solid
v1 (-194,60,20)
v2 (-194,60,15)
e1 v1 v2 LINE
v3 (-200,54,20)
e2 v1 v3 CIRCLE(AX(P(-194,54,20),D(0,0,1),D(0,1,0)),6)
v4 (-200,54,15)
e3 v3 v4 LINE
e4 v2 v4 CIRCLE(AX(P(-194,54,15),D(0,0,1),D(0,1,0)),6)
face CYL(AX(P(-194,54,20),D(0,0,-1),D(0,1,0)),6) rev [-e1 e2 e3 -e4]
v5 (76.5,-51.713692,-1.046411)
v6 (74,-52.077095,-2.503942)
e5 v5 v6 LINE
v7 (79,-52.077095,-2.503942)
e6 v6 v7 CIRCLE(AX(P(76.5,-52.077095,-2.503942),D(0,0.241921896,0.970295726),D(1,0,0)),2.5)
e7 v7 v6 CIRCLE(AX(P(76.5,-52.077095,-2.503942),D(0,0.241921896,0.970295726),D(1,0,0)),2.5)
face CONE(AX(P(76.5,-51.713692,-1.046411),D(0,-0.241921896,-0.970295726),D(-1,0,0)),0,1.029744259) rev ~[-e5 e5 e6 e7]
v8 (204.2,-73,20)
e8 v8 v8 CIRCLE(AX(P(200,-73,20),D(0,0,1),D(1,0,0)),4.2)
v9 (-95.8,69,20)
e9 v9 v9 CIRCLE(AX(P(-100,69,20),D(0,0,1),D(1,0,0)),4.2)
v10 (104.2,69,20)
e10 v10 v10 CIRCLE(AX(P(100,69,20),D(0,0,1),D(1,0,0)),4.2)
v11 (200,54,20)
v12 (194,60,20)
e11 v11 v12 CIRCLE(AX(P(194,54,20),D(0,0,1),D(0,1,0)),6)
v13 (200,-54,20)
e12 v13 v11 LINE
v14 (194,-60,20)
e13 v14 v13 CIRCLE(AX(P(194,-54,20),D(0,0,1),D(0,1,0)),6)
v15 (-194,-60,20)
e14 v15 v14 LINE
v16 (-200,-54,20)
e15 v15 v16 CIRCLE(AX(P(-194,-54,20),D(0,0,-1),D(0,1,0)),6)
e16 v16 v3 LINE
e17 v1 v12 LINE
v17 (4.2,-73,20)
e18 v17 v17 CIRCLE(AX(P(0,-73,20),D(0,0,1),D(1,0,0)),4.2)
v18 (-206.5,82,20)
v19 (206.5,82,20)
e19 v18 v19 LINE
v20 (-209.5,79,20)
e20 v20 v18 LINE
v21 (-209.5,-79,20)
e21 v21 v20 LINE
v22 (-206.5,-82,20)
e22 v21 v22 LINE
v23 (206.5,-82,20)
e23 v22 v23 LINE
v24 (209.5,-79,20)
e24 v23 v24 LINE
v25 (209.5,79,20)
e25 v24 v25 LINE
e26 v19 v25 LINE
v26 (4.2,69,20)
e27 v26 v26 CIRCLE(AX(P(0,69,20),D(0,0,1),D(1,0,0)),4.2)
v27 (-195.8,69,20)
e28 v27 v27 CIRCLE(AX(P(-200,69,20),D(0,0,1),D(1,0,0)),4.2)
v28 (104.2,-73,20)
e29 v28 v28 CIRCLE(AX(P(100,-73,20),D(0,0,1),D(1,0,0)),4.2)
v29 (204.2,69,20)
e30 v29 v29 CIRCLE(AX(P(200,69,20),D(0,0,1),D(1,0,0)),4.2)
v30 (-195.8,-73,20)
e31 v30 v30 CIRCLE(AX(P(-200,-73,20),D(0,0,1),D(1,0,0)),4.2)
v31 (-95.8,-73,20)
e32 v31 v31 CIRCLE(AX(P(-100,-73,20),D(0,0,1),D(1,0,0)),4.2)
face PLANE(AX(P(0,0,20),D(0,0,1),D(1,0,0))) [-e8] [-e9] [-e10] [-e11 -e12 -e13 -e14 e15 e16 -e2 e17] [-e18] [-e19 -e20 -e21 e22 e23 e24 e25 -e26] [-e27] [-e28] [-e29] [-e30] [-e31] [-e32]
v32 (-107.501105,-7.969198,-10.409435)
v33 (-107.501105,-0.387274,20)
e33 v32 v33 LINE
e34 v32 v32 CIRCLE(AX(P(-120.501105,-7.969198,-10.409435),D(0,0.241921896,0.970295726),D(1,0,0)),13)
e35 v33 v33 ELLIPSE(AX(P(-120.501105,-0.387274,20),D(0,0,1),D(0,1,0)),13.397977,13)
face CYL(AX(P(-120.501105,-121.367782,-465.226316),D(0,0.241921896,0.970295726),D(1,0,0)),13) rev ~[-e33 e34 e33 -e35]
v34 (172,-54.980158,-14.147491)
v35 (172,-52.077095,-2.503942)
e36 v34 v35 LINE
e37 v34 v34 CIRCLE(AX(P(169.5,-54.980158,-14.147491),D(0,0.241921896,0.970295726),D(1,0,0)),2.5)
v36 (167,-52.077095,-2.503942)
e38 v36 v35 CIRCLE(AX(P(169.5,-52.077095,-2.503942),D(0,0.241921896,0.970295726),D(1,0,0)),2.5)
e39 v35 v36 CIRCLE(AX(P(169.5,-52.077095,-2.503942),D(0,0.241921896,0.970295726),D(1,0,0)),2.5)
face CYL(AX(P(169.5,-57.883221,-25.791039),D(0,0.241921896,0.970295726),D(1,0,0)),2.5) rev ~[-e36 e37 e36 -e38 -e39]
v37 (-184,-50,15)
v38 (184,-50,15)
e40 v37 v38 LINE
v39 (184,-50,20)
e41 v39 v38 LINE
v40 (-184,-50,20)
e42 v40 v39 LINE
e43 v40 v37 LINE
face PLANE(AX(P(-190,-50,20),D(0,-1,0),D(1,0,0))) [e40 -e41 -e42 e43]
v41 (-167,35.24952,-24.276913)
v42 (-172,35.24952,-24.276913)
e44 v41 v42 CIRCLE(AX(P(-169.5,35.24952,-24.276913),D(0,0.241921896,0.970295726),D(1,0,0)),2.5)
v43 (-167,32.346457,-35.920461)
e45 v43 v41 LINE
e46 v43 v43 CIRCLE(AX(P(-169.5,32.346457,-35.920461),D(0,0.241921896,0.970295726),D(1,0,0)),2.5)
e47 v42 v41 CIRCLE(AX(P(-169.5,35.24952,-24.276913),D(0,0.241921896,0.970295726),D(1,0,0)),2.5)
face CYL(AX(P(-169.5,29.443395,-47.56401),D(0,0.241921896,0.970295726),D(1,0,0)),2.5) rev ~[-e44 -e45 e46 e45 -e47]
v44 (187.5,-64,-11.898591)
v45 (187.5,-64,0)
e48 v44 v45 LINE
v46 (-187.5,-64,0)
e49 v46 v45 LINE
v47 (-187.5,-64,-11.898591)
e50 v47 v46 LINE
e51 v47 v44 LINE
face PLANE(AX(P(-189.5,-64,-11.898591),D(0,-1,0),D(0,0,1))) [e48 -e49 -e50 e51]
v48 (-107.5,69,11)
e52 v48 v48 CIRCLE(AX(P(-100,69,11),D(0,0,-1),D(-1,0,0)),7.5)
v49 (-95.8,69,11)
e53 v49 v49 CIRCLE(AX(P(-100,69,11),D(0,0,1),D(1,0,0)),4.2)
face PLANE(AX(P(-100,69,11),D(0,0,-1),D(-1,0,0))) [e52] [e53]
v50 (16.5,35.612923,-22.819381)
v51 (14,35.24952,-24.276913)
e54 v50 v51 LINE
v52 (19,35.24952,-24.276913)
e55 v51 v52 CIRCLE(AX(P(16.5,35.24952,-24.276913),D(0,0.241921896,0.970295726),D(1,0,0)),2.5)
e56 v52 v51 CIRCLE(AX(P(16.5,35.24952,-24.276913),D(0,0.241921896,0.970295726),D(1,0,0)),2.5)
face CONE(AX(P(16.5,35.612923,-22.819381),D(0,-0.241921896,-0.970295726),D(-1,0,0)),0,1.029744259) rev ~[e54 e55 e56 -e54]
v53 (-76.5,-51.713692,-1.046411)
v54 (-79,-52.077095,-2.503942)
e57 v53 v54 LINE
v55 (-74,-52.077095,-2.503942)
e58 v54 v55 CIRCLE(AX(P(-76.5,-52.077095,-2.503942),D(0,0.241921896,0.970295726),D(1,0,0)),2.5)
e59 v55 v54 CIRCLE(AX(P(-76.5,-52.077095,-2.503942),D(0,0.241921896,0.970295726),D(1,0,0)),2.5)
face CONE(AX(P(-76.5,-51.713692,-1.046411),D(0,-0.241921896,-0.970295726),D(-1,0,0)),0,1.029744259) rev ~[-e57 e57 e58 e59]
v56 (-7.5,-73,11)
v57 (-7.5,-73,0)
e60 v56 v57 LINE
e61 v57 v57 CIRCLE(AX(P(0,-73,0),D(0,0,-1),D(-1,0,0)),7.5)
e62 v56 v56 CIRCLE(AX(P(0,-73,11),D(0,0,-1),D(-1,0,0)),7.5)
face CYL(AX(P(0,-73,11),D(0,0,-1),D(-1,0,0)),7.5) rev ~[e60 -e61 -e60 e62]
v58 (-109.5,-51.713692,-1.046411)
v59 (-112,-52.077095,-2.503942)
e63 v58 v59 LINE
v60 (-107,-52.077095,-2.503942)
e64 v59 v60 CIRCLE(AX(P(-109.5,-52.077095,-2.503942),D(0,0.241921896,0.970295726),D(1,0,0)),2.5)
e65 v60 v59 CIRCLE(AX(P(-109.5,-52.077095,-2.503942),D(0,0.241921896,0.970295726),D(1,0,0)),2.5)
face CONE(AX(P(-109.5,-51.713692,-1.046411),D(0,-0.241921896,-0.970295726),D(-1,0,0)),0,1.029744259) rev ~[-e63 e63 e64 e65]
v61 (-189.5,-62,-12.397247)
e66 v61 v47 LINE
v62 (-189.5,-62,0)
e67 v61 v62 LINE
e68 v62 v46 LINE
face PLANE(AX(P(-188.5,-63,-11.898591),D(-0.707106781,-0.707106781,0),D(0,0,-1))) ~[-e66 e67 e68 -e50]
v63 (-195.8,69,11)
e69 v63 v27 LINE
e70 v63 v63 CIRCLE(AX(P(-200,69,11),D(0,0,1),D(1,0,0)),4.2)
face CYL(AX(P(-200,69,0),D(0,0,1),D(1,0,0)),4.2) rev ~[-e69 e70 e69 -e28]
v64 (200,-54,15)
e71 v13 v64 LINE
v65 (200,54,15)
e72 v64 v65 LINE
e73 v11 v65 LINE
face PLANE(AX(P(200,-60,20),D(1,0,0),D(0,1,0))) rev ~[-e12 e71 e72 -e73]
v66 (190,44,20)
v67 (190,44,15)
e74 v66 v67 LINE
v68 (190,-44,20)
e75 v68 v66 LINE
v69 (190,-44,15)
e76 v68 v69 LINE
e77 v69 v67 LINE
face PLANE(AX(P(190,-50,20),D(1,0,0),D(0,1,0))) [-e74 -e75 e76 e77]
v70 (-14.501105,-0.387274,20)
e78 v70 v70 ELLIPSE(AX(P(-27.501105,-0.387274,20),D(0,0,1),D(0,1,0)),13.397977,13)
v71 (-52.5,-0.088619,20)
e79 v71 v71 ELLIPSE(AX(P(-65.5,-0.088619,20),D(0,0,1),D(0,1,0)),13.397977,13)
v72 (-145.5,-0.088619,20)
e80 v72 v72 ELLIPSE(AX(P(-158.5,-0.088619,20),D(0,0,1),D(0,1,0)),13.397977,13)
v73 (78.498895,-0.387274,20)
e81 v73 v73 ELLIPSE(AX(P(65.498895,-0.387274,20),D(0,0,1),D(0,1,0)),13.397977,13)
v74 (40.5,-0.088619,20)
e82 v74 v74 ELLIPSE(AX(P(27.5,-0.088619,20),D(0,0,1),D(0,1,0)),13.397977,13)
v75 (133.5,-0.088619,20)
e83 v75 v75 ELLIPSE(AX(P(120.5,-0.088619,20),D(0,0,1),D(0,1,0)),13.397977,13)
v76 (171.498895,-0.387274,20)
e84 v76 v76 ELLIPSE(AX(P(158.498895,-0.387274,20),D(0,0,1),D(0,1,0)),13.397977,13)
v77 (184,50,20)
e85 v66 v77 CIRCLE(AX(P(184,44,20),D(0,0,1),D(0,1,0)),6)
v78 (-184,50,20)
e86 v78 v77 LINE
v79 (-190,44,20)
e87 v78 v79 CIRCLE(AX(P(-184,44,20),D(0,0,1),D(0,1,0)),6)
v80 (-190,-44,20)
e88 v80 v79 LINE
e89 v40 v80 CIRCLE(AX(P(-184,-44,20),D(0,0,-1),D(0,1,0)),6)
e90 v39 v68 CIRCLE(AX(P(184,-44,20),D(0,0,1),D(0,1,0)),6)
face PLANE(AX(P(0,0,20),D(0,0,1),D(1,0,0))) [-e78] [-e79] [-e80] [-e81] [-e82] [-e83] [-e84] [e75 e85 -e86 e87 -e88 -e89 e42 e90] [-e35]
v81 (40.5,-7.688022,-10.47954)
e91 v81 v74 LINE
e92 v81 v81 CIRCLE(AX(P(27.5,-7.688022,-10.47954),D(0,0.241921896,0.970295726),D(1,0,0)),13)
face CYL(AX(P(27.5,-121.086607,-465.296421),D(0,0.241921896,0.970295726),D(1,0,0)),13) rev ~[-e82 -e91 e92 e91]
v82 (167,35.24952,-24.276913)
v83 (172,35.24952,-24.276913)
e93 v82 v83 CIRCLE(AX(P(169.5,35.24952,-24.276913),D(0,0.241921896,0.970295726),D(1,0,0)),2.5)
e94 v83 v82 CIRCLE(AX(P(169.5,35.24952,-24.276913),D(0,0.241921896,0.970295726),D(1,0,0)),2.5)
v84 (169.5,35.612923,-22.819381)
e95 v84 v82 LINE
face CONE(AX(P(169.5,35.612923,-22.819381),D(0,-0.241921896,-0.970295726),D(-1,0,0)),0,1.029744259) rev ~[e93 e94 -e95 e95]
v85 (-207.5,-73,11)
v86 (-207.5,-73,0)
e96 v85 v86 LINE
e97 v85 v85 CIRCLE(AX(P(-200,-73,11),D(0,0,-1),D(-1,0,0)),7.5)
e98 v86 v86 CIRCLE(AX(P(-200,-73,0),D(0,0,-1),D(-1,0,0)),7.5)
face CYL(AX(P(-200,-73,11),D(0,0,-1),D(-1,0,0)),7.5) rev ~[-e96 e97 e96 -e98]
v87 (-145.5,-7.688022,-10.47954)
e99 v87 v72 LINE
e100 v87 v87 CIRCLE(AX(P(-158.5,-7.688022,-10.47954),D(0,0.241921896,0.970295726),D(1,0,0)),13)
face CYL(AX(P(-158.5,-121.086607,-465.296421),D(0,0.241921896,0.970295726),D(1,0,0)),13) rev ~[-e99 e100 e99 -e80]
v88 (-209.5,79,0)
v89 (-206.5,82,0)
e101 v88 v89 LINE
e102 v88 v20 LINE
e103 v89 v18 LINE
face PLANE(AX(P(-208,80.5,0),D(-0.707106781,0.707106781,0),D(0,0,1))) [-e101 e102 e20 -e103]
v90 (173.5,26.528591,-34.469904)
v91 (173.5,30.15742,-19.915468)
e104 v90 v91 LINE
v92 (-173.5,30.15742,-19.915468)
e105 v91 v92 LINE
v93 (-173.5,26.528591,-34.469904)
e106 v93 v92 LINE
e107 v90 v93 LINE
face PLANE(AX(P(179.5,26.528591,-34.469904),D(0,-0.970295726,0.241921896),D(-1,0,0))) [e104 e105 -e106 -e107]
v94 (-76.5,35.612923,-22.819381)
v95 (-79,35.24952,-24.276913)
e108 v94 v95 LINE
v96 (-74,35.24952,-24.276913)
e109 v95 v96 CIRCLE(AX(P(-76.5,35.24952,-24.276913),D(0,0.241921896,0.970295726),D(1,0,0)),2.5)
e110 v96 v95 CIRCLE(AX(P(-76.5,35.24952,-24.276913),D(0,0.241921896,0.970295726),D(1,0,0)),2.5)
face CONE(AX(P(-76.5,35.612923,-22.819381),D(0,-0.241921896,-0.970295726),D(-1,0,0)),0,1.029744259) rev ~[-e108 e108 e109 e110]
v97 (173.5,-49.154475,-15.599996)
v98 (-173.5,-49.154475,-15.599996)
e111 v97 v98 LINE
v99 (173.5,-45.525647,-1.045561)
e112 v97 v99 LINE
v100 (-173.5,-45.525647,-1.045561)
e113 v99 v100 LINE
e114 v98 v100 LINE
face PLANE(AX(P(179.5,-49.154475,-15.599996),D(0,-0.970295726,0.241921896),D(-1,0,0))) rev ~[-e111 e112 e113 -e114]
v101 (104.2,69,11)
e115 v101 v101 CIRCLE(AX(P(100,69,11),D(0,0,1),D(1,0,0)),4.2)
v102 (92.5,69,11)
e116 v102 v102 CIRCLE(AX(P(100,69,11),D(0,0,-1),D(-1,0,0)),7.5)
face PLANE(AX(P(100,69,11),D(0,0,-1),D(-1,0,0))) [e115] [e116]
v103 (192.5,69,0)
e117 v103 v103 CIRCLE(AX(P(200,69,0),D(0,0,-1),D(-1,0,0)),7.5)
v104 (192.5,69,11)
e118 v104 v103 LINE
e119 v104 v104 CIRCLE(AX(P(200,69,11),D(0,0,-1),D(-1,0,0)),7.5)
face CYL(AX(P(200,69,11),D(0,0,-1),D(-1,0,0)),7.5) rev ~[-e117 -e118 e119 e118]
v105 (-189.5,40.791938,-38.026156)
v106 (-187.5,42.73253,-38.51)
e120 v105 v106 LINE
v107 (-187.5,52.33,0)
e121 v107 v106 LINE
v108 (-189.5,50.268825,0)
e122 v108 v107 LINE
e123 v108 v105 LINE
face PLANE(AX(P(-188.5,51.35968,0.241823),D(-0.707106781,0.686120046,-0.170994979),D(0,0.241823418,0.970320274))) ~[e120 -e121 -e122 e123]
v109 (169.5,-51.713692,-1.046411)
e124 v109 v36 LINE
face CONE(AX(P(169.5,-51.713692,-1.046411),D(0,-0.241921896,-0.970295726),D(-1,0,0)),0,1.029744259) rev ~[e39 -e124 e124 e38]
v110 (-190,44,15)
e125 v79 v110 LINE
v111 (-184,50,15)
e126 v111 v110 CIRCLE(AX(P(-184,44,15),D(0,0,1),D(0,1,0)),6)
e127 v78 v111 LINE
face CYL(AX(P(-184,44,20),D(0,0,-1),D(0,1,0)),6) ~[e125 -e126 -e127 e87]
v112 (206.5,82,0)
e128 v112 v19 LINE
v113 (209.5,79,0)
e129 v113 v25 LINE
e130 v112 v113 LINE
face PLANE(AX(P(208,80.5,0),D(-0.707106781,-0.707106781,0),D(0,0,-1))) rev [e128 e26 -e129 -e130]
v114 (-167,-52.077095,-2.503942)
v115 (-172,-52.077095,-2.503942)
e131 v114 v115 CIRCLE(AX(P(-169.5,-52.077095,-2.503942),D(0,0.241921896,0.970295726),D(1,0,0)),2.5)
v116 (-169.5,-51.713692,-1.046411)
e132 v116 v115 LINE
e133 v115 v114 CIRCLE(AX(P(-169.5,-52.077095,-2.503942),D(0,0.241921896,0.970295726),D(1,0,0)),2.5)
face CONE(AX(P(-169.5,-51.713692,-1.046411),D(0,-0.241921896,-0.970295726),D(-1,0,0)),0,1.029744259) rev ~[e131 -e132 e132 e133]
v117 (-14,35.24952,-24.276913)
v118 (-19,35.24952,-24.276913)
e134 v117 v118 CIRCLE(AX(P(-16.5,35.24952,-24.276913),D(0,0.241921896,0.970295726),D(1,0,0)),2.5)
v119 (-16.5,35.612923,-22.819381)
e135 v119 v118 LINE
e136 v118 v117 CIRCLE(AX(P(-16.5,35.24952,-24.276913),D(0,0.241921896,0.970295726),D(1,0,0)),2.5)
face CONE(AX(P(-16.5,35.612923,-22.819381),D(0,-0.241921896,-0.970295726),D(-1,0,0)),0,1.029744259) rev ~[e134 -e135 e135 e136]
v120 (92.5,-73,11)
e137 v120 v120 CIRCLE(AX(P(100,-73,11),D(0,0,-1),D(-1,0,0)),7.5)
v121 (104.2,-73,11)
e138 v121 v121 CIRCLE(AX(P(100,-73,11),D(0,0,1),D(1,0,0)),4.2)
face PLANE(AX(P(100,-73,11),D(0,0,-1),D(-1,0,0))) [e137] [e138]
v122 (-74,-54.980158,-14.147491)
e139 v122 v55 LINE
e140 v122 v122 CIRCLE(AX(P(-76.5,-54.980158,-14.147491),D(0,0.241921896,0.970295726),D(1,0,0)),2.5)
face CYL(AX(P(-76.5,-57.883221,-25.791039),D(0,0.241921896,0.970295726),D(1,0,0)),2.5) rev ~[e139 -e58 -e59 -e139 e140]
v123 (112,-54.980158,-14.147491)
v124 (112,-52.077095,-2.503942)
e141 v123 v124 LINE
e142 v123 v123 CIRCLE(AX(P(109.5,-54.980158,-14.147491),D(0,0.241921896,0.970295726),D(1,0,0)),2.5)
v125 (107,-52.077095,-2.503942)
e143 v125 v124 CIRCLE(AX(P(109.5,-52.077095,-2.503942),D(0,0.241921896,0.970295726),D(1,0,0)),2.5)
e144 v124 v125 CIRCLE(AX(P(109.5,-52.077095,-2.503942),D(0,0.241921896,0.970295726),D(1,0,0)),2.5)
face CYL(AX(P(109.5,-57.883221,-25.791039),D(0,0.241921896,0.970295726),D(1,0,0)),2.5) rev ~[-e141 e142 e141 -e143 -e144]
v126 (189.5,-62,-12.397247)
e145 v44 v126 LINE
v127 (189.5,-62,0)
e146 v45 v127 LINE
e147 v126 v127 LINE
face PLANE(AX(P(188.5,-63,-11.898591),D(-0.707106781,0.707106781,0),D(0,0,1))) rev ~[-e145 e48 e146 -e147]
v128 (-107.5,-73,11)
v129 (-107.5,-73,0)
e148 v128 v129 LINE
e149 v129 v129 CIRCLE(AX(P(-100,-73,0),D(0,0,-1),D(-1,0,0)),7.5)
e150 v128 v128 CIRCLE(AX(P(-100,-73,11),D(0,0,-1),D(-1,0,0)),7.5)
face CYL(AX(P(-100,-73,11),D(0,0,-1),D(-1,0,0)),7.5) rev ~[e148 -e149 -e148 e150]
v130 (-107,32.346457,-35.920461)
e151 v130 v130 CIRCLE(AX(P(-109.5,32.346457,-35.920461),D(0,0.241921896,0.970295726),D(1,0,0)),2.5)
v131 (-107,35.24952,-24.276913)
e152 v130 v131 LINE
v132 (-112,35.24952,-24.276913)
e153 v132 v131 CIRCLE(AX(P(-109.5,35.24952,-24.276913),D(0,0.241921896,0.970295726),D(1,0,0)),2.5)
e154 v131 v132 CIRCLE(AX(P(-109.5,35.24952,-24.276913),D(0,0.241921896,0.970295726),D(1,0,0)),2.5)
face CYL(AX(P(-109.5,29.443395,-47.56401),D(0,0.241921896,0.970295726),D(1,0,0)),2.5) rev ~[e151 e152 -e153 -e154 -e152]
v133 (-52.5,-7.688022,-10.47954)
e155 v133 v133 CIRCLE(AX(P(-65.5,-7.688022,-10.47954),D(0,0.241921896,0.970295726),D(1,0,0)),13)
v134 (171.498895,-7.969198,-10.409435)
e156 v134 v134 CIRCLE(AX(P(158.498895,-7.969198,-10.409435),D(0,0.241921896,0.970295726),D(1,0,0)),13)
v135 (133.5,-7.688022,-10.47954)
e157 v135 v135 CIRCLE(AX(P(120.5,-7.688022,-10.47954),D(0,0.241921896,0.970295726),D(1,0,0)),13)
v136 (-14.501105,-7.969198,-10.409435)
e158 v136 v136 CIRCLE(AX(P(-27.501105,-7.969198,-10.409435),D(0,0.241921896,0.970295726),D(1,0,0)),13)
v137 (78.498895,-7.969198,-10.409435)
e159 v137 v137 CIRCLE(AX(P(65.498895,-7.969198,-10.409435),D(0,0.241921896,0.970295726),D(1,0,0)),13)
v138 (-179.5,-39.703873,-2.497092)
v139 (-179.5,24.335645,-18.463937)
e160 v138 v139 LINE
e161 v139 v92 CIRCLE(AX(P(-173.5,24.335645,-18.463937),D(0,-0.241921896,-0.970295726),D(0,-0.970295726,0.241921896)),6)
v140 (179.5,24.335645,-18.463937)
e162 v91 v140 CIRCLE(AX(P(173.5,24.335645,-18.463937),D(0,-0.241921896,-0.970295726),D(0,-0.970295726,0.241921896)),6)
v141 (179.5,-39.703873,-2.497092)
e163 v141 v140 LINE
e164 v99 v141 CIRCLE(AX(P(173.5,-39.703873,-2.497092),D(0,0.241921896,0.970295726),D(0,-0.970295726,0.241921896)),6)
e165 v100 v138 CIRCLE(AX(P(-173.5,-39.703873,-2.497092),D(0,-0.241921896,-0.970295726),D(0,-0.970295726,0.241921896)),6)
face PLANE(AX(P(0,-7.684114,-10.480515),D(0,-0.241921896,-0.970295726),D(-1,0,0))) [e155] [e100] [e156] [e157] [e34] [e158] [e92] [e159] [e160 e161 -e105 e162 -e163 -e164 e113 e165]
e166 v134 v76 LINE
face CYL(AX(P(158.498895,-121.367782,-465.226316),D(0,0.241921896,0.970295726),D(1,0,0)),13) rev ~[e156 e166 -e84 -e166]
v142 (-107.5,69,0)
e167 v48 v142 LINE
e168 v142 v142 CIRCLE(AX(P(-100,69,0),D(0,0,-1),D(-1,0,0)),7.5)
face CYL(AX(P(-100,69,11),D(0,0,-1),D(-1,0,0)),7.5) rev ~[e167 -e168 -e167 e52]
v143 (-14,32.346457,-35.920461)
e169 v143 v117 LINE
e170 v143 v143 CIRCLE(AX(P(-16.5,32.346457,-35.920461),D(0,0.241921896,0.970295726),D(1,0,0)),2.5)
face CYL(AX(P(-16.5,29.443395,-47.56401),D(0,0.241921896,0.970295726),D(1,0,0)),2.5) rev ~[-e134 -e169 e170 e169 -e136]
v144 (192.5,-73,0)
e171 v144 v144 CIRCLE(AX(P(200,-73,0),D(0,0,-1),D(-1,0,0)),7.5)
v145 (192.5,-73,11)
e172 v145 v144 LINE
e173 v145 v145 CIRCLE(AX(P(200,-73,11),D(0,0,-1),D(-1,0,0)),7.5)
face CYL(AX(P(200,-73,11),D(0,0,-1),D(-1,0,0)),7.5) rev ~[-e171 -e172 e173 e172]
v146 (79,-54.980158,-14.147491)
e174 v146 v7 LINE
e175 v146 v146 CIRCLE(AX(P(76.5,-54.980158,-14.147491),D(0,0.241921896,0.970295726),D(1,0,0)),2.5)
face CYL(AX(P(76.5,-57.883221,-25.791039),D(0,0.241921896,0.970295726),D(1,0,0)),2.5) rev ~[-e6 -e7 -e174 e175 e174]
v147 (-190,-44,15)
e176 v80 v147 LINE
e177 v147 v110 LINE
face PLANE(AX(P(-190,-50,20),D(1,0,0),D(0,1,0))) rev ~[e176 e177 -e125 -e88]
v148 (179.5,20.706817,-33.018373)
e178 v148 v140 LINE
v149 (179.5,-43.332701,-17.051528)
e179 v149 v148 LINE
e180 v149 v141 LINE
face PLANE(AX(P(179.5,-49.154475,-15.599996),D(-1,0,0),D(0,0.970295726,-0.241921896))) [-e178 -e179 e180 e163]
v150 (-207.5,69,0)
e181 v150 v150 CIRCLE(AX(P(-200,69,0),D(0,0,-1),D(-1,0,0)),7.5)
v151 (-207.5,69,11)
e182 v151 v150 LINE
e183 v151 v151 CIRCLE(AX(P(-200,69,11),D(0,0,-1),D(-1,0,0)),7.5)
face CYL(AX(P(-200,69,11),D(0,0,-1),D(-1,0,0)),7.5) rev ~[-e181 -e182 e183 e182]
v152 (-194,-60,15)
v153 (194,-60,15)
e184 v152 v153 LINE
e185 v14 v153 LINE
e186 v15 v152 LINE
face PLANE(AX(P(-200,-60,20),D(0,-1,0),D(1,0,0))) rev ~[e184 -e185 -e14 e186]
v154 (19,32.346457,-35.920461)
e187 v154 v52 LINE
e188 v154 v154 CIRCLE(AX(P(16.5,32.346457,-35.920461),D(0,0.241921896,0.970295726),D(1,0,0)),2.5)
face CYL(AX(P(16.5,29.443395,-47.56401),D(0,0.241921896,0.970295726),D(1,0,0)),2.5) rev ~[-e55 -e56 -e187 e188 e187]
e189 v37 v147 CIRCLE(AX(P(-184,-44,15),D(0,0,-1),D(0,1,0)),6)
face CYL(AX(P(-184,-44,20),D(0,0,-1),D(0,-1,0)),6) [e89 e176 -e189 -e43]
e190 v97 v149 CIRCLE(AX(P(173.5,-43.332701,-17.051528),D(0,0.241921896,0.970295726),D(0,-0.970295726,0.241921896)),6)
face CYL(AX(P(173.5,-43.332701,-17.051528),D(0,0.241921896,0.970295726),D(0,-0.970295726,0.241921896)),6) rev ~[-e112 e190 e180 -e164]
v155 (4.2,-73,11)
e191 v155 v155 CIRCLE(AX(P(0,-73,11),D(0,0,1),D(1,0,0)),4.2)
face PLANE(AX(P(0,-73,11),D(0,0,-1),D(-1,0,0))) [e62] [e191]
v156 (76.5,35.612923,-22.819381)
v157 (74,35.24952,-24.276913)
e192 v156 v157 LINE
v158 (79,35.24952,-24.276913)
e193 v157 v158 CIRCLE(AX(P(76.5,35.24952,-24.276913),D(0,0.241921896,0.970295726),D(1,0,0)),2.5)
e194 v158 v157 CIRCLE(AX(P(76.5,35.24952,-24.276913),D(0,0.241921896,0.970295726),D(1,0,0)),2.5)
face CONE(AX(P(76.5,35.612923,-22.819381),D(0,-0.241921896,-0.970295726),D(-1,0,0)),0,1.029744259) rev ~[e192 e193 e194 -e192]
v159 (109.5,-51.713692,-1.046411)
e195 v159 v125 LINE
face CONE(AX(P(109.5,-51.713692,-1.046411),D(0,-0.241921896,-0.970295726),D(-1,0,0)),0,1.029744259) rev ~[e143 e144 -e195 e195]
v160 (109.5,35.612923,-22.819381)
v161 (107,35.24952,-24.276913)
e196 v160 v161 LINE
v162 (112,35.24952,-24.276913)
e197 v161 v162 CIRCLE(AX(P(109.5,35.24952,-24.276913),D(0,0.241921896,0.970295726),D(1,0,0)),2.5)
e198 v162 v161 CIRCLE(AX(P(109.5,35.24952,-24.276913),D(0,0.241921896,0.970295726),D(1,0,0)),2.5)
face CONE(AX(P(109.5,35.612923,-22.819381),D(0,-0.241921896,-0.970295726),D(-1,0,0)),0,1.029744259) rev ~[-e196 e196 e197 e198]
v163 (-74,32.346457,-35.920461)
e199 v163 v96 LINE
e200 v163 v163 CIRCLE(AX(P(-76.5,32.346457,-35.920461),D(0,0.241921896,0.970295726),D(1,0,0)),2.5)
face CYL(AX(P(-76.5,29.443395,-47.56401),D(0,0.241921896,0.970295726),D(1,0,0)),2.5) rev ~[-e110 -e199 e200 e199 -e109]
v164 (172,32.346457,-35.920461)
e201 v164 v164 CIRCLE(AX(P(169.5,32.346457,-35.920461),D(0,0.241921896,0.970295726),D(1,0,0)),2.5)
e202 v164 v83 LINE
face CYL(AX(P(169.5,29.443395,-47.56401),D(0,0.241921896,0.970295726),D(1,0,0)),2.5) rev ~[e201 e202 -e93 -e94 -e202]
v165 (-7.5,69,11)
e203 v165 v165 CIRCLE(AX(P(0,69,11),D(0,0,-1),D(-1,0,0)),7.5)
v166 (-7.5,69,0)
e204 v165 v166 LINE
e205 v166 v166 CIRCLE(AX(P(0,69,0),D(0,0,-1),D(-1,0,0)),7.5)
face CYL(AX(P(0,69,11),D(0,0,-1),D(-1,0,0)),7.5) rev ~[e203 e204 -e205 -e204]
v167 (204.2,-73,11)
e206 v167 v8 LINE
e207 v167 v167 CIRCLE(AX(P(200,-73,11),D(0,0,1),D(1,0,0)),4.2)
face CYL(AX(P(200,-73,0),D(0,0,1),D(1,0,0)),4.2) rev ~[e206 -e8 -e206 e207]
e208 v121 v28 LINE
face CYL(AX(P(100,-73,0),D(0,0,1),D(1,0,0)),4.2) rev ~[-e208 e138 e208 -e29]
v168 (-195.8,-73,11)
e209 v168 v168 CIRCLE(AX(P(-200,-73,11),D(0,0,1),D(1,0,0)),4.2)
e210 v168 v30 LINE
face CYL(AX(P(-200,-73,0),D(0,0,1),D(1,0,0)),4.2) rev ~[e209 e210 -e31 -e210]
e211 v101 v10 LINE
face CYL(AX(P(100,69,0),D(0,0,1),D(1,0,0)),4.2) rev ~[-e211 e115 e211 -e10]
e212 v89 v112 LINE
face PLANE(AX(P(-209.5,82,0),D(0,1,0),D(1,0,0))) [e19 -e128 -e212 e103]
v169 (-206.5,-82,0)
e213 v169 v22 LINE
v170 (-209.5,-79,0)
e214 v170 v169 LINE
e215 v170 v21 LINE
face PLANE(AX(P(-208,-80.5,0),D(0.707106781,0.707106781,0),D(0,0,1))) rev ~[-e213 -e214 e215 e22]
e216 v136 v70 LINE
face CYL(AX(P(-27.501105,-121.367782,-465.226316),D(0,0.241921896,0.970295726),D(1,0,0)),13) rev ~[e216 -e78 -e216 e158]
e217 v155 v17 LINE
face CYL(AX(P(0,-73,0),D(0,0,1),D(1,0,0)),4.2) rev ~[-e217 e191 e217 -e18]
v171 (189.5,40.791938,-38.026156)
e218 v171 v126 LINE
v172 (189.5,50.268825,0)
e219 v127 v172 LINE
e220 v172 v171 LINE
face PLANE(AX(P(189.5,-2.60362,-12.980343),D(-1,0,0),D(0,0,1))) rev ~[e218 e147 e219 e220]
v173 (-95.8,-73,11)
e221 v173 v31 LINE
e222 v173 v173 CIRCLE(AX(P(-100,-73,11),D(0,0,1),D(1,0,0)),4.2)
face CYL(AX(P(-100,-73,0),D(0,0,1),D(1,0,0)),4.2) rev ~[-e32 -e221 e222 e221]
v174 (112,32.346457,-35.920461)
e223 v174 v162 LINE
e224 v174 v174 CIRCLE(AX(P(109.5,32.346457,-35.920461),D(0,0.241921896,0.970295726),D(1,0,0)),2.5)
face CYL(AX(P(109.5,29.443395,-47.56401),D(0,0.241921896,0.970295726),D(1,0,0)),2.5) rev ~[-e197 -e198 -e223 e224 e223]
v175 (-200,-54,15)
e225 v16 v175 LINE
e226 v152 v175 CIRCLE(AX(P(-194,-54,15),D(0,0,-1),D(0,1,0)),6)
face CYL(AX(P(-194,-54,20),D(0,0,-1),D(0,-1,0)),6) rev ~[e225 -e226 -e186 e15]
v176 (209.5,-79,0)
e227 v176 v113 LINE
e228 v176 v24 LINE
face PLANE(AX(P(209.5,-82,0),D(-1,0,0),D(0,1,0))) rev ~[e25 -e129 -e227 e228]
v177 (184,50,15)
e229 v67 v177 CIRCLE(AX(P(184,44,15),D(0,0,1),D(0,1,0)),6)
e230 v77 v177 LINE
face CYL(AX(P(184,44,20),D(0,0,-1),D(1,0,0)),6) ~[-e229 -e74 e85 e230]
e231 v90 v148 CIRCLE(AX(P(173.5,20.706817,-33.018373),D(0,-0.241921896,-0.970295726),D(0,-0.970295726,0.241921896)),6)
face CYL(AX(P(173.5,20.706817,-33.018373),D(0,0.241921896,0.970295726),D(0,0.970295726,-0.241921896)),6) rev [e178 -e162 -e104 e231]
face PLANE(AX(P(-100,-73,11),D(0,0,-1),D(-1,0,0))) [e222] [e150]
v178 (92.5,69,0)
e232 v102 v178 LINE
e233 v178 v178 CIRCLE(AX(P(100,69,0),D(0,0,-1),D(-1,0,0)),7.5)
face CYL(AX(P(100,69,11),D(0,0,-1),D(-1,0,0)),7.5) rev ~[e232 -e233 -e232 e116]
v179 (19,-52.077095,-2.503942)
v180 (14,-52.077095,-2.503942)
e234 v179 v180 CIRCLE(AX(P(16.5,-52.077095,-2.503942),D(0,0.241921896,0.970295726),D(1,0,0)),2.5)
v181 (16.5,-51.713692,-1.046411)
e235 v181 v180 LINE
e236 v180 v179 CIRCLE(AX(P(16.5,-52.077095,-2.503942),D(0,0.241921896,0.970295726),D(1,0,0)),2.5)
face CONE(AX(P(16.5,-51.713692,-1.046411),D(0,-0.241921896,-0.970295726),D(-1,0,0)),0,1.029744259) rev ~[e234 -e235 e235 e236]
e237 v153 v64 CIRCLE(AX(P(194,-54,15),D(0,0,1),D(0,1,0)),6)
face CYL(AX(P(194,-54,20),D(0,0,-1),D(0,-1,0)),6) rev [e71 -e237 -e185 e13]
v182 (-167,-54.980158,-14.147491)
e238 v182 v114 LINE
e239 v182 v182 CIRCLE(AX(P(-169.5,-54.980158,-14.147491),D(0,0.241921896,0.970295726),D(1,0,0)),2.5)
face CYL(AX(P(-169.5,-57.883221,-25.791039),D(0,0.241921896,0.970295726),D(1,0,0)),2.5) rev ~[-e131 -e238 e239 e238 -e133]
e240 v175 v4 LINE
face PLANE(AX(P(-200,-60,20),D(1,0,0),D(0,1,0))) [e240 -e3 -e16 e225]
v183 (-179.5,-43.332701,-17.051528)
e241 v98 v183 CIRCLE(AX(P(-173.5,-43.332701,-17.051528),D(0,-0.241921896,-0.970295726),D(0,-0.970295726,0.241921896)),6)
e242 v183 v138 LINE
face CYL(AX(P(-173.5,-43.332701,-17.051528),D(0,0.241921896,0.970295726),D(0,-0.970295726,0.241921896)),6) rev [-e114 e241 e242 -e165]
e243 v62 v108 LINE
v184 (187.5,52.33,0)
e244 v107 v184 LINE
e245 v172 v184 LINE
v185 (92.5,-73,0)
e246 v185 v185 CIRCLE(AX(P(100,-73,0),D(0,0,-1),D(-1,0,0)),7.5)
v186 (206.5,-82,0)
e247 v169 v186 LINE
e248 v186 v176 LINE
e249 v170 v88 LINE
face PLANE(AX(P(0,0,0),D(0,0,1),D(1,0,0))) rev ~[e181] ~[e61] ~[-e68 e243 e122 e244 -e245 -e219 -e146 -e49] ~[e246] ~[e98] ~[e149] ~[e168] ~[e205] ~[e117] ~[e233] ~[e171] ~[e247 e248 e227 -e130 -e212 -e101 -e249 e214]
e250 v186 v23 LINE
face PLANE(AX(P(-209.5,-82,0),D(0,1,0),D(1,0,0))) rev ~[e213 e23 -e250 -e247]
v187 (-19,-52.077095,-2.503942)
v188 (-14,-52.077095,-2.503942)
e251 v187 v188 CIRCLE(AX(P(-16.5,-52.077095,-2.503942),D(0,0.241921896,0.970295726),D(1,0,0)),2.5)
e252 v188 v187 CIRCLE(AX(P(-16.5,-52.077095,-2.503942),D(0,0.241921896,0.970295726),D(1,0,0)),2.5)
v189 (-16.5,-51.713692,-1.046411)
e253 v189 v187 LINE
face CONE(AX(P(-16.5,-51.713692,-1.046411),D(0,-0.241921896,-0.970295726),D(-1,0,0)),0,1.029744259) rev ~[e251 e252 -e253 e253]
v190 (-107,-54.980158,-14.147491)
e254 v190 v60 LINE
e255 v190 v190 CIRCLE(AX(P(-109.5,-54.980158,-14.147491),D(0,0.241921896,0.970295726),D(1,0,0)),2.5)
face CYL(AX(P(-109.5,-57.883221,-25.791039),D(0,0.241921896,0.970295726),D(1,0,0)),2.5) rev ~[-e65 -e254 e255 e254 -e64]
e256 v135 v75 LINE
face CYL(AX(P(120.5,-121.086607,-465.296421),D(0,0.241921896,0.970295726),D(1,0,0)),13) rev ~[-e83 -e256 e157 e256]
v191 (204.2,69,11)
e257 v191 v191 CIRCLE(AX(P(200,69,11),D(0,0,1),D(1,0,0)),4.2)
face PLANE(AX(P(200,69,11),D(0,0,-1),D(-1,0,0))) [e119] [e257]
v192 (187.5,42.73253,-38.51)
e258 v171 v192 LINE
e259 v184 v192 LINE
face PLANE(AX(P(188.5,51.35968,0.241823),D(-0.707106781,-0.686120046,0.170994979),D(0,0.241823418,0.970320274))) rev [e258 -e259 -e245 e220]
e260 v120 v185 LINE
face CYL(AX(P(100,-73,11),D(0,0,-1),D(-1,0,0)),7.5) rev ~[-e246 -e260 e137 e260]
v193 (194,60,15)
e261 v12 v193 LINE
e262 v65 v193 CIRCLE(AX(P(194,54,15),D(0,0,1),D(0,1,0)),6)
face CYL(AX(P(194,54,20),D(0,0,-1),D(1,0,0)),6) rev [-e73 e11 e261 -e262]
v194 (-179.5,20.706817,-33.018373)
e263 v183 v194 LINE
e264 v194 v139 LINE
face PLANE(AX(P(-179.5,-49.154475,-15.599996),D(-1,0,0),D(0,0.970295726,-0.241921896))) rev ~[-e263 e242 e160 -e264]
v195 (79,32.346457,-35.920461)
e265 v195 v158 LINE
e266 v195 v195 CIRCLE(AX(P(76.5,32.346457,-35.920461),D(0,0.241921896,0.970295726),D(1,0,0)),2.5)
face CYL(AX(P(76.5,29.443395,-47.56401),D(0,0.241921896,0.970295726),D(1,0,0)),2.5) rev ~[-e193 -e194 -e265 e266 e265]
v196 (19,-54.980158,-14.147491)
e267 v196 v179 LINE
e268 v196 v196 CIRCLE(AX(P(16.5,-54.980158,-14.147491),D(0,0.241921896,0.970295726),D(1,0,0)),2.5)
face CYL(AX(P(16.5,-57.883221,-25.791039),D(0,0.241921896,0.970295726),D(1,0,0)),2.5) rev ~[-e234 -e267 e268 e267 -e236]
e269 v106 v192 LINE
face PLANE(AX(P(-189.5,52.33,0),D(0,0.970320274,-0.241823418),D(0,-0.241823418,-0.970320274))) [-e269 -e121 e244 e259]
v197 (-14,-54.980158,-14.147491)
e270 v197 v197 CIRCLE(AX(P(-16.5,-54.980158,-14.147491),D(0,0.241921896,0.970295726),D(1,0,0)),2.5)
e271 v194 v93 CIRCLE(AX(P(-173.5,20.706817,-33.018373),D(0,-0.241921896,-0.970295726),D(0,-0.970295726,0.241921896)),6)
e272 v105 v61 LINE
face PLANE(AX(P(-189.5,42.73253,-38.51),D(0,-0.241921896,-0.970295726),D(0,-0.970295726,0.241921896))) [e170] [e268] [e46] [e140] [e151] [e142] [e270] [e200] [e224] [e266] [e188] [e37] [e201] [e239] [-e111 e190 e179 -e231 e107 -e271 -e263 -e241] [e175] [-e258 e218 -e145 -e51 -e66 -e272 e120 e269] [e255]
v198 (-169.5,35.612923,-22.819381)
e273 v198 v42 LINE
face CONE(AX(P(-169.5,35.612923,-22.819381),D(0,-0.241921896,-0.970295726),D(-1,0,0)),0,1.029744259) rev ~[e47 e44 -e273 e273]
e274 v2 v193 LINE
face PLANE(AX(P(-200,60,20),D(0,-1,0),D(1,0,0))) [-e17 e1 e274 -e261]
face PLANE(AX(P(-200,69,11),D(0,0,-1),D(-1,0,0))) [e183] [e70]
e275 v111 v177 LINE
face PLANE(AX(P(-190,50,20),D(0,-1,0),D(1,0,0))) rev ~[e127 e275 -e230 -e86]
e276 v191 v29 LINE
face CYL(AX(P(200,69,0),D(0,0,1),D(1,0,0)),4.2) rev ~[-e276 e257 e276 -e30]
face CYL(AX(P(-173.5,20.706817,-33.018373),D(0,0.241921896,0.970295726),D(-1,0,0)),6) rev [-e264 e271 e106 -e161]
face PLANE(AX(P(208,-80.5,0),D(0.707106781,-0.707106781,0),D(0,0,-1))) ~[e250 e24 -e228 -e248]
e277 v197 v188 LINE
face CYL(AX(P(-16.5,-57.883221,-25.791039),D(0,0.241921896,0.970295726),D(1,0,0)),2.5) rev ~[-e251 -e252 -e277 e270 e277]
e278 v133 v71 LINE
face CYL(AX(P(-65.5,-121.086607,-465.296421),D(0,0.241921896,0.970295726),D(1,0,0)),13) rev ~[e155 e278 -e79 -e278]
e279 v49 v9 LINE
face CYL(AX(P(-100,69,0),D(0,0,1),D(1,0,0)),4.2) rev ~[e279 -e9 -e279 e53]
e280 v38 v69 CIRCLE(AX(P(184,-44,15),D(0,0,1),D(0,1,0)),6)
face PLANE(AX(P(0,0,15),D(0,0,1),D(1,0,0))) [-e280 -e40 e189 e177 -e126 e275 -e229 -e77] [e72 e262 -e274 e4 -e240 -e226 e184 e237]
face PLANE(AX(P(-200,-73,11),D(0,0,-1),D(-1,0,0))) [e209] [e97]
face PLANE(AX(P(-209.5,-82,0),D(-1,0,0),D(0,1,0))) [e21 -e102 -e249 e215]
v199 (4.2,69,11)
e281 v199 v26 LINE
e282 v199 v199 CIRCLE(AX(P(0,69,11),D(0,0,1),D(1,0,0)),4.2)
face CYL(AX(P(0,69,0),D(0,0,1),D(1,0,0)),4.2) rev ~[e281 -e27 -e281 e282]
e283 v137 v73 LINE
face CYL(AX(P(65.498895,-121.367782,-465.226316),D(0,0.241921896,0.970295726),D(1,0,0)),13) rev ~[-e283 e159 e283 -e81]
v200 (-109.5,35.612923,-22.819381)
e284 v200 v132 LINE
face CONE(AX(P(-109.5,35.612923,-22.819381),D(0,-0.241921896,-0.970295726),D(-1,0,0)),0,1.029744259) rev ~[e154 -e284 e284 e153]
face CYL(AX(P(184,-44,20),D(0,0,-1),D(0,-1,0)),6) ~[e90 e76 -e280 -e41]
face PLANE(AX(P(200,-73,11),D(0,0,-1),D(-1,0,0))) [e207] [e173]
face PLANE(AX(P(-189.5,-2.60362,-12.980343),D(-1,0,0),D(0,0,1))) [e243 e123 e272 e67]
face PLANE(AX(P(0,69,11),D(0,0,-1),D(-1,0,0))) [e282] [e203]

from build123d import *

# Parameters (mm, degrees)
SKETCH1_W             = 419
SKETCH1_H             = 164
BOSS_EXTRUDE1_DEPTH   = 20
SKETCH2_W             = 400
SKETCH2_H             = 120
SKETCH2_W_2           = 380
SKETCH2_H_2           = 100
CUT_EXTRUDE1_DEPTH    = 5
FILLET1_R             = 6
CHAMFER1_SIZE         = 3
HOLE1_D               = 8.4
HOLE1_CBORE_D         = 15
HOLE1_CBORE_DEPTH     = 11
BOSS_EXTRUDE2_DEPTH   = 379
CHAMFER2_SIZE         = 2
HOLE2_D               = 26
M6_TAPPED_HOLE1_D     = 5
M6_TAPPED_HOLE1_DEPTH = 12
M6_TAPPED_HOLE1_TIP   = 1.502151548
SKETCH12_W            = 359
SKETCH12_H            = 78
CUT_EXTRUDE2_DEPTH    = 15
FILLET2_R             = 6


with BuildPart() as part:
    # Sketch1 → Boss-Extrude1 (new body)
    with BuildSketch(Plane.XY):
        Rectangle(SKETCH1_W, SKETCH1_H)
    extrude(amount=BOSS_EXTRUDE1_DEPTH)

    # Sketch2 → Cut-Extrude1 (cut)
    with BuildSketch(Plane.XY.offset(20)):
        Rectangle(SKETCH2_W, SKETCH2_H)
        Rectangle(SKETCH2_W_2, SKETCH2_H_2, mode=Mode.SUBTRACT)
    extrude(amount=-CUT_EXTRUDE1_DEPTH, mode=Mode.SUBTRACT)

    # Fillet1
    fillet1_edges = [part.edges().sort_by_distance(p)[0] for p in [
        (200, 60, 17.5),
        (200, -60, 17.5),
        (-200, -60, 17.5),
        (-200, 60, 17.5),
        (190, -50, 17.5),
        (-190, -50, 17.5),
        (-190, 50, 17.5),
        (190, 50, 17.5),
    ]]
    fillet(fillet1_edges, radius=FILLET1_R)

    # Chamfer1
    chamfer1_edges = [part.edges().sort_by_distance(p)[0] for p in [
        (209.5, -82, 10),
        (-209.5, -82, 10),
        (-209.5, 82, 10),
        (209.5, 82, 10),
    ]]
    chamfer(chamfer1_edges, length=CHAMFER1_SIZE)

    # Hole1 (through all)
    with Locations(Plane(origin=(0, 0, 0), x_dir=(-1, 0, 0), z_dir=(0, 0, -1))):
        with Locations((-200, 69), (-200, -73), (-100, -73), (0, -73), (100, -73), (200, -73), (200, 69), (100, 69), (0, 69), (-100, 69)):
            CounterBoreHole(HOLE1_D / 2, HOLE1_CBORE_D / 2, HOLE1_CBORE_DEPTH)

    # Sketch6 → Boss-Extrude2 (add)
    with BuildSketch(Plane.ZY.offset(189.5)):
        Polygon((0, 52.33), (-38.51, 42.73252989), (-11.898591484, -64), (0, -64), align=None)
    extrude(amount=-BOSS_EXTRUDE2_DEPTH)

    # Chamfer2
    chamfer2_edges = [part.edges().sort_by_distance(p)[0] for p in [
        (189.5, -64, -5.949295742),
        (189.5, 47.531264945, -19.255),
        (-189.5, 47.531264945, -19.255),
        (-189.5, -64, -5.949295742),
    ]]
    chamfer(chamfer2_edges, length=CHAMFER2_SIZE)

    # Hole2 (through all)
    with Locations(Plane(origin=(0, -6.538702198, -26.225302106), x_dir=(-1, 0, 0), z_dir=(0, -0.24192189559966124, -0.970295726275998))):
        with Locations((158.5, -4.924424644), (120.501104945, -5.214208356), (65.5, -4.924424644), (27.501104945, -5.214208356), (-27.5, -4.924424644), (-65.498895055, -5.214208356), (-120.5, -4.924424644), (-158.498895055, -5.214208356)):
            Hole(HOLE2_D / 2)

    # M6 Tapped Hole1
    with Locations(Plane(origin=(0, -6.538702198, -26.225302106), x_dir=(-1, 0, 0), z_dir=(0, -0.24192189559966124, -0.970295726275998))):
        with Locations((-169.5, 40.075575356), (-109.5, 40.075575356), (-76.5, 40.075575356), (-16.5, 40.075575356), (16.5, 40.075575356), (76.5, 40.075575356), (109.5, 40.075575356), (169.5, 40.075575356), (169.5, -49.924424644), (109.5, -49.924424644), (76.5, -49.924424644), (16.5, -49.924424644), (-16.5, -49.924424644), (-76.5, -49.924424644), (-109.5, -49.924424644), (-169.5, -49.924424644)):
            Hole(M6_TAPPED_HOLE1_D / 2, depth=M6_TAPPED_HOLE1_DEPTH)
            with Locations((0, 0, -(M6_TAPPED_HOLE1_DEPTH + M6_TAPPED_HOLE1_TIP / 2))):  # 118° drill point
                Cone(0, M6_TAPPED_HOLE1_D / 2, M6_TAPPED_HOLE1_TIP, mode=Mode.SUBTRACT)

    # Sketch12 → Cut-Extrude2 (cut)
    with BuildSketch(Plane(origin=(0, -6.538702198, -26.225302106), x_dir=(-1, 0, 0), z_dir=(0, -0.24192189559966124, -0.970295726275998))):
        with Locations((0, -4.920396675)):
            Rectangle(SKETCH12_W, SKETCH12_H)
    extrude(amount=-CUT_EXTRUDE2_DEPTH, mode=Mode.SUBTRACT)

    # Fillet2
    fillet2_edges = [part.edges().sort_by_distance(p)[0] for p in [
        (179.5, -47.340061171, -8.32277854),
        (179.5, 28.343005479, -27.192686396),
        (-179.5, 28.343005479, -27.192686396),
        (-179.5, -47.340061171, -8.32277854),
    ]]
    fillet(fillet2_edges, radius=FILLET2_R)


solid = part.part
